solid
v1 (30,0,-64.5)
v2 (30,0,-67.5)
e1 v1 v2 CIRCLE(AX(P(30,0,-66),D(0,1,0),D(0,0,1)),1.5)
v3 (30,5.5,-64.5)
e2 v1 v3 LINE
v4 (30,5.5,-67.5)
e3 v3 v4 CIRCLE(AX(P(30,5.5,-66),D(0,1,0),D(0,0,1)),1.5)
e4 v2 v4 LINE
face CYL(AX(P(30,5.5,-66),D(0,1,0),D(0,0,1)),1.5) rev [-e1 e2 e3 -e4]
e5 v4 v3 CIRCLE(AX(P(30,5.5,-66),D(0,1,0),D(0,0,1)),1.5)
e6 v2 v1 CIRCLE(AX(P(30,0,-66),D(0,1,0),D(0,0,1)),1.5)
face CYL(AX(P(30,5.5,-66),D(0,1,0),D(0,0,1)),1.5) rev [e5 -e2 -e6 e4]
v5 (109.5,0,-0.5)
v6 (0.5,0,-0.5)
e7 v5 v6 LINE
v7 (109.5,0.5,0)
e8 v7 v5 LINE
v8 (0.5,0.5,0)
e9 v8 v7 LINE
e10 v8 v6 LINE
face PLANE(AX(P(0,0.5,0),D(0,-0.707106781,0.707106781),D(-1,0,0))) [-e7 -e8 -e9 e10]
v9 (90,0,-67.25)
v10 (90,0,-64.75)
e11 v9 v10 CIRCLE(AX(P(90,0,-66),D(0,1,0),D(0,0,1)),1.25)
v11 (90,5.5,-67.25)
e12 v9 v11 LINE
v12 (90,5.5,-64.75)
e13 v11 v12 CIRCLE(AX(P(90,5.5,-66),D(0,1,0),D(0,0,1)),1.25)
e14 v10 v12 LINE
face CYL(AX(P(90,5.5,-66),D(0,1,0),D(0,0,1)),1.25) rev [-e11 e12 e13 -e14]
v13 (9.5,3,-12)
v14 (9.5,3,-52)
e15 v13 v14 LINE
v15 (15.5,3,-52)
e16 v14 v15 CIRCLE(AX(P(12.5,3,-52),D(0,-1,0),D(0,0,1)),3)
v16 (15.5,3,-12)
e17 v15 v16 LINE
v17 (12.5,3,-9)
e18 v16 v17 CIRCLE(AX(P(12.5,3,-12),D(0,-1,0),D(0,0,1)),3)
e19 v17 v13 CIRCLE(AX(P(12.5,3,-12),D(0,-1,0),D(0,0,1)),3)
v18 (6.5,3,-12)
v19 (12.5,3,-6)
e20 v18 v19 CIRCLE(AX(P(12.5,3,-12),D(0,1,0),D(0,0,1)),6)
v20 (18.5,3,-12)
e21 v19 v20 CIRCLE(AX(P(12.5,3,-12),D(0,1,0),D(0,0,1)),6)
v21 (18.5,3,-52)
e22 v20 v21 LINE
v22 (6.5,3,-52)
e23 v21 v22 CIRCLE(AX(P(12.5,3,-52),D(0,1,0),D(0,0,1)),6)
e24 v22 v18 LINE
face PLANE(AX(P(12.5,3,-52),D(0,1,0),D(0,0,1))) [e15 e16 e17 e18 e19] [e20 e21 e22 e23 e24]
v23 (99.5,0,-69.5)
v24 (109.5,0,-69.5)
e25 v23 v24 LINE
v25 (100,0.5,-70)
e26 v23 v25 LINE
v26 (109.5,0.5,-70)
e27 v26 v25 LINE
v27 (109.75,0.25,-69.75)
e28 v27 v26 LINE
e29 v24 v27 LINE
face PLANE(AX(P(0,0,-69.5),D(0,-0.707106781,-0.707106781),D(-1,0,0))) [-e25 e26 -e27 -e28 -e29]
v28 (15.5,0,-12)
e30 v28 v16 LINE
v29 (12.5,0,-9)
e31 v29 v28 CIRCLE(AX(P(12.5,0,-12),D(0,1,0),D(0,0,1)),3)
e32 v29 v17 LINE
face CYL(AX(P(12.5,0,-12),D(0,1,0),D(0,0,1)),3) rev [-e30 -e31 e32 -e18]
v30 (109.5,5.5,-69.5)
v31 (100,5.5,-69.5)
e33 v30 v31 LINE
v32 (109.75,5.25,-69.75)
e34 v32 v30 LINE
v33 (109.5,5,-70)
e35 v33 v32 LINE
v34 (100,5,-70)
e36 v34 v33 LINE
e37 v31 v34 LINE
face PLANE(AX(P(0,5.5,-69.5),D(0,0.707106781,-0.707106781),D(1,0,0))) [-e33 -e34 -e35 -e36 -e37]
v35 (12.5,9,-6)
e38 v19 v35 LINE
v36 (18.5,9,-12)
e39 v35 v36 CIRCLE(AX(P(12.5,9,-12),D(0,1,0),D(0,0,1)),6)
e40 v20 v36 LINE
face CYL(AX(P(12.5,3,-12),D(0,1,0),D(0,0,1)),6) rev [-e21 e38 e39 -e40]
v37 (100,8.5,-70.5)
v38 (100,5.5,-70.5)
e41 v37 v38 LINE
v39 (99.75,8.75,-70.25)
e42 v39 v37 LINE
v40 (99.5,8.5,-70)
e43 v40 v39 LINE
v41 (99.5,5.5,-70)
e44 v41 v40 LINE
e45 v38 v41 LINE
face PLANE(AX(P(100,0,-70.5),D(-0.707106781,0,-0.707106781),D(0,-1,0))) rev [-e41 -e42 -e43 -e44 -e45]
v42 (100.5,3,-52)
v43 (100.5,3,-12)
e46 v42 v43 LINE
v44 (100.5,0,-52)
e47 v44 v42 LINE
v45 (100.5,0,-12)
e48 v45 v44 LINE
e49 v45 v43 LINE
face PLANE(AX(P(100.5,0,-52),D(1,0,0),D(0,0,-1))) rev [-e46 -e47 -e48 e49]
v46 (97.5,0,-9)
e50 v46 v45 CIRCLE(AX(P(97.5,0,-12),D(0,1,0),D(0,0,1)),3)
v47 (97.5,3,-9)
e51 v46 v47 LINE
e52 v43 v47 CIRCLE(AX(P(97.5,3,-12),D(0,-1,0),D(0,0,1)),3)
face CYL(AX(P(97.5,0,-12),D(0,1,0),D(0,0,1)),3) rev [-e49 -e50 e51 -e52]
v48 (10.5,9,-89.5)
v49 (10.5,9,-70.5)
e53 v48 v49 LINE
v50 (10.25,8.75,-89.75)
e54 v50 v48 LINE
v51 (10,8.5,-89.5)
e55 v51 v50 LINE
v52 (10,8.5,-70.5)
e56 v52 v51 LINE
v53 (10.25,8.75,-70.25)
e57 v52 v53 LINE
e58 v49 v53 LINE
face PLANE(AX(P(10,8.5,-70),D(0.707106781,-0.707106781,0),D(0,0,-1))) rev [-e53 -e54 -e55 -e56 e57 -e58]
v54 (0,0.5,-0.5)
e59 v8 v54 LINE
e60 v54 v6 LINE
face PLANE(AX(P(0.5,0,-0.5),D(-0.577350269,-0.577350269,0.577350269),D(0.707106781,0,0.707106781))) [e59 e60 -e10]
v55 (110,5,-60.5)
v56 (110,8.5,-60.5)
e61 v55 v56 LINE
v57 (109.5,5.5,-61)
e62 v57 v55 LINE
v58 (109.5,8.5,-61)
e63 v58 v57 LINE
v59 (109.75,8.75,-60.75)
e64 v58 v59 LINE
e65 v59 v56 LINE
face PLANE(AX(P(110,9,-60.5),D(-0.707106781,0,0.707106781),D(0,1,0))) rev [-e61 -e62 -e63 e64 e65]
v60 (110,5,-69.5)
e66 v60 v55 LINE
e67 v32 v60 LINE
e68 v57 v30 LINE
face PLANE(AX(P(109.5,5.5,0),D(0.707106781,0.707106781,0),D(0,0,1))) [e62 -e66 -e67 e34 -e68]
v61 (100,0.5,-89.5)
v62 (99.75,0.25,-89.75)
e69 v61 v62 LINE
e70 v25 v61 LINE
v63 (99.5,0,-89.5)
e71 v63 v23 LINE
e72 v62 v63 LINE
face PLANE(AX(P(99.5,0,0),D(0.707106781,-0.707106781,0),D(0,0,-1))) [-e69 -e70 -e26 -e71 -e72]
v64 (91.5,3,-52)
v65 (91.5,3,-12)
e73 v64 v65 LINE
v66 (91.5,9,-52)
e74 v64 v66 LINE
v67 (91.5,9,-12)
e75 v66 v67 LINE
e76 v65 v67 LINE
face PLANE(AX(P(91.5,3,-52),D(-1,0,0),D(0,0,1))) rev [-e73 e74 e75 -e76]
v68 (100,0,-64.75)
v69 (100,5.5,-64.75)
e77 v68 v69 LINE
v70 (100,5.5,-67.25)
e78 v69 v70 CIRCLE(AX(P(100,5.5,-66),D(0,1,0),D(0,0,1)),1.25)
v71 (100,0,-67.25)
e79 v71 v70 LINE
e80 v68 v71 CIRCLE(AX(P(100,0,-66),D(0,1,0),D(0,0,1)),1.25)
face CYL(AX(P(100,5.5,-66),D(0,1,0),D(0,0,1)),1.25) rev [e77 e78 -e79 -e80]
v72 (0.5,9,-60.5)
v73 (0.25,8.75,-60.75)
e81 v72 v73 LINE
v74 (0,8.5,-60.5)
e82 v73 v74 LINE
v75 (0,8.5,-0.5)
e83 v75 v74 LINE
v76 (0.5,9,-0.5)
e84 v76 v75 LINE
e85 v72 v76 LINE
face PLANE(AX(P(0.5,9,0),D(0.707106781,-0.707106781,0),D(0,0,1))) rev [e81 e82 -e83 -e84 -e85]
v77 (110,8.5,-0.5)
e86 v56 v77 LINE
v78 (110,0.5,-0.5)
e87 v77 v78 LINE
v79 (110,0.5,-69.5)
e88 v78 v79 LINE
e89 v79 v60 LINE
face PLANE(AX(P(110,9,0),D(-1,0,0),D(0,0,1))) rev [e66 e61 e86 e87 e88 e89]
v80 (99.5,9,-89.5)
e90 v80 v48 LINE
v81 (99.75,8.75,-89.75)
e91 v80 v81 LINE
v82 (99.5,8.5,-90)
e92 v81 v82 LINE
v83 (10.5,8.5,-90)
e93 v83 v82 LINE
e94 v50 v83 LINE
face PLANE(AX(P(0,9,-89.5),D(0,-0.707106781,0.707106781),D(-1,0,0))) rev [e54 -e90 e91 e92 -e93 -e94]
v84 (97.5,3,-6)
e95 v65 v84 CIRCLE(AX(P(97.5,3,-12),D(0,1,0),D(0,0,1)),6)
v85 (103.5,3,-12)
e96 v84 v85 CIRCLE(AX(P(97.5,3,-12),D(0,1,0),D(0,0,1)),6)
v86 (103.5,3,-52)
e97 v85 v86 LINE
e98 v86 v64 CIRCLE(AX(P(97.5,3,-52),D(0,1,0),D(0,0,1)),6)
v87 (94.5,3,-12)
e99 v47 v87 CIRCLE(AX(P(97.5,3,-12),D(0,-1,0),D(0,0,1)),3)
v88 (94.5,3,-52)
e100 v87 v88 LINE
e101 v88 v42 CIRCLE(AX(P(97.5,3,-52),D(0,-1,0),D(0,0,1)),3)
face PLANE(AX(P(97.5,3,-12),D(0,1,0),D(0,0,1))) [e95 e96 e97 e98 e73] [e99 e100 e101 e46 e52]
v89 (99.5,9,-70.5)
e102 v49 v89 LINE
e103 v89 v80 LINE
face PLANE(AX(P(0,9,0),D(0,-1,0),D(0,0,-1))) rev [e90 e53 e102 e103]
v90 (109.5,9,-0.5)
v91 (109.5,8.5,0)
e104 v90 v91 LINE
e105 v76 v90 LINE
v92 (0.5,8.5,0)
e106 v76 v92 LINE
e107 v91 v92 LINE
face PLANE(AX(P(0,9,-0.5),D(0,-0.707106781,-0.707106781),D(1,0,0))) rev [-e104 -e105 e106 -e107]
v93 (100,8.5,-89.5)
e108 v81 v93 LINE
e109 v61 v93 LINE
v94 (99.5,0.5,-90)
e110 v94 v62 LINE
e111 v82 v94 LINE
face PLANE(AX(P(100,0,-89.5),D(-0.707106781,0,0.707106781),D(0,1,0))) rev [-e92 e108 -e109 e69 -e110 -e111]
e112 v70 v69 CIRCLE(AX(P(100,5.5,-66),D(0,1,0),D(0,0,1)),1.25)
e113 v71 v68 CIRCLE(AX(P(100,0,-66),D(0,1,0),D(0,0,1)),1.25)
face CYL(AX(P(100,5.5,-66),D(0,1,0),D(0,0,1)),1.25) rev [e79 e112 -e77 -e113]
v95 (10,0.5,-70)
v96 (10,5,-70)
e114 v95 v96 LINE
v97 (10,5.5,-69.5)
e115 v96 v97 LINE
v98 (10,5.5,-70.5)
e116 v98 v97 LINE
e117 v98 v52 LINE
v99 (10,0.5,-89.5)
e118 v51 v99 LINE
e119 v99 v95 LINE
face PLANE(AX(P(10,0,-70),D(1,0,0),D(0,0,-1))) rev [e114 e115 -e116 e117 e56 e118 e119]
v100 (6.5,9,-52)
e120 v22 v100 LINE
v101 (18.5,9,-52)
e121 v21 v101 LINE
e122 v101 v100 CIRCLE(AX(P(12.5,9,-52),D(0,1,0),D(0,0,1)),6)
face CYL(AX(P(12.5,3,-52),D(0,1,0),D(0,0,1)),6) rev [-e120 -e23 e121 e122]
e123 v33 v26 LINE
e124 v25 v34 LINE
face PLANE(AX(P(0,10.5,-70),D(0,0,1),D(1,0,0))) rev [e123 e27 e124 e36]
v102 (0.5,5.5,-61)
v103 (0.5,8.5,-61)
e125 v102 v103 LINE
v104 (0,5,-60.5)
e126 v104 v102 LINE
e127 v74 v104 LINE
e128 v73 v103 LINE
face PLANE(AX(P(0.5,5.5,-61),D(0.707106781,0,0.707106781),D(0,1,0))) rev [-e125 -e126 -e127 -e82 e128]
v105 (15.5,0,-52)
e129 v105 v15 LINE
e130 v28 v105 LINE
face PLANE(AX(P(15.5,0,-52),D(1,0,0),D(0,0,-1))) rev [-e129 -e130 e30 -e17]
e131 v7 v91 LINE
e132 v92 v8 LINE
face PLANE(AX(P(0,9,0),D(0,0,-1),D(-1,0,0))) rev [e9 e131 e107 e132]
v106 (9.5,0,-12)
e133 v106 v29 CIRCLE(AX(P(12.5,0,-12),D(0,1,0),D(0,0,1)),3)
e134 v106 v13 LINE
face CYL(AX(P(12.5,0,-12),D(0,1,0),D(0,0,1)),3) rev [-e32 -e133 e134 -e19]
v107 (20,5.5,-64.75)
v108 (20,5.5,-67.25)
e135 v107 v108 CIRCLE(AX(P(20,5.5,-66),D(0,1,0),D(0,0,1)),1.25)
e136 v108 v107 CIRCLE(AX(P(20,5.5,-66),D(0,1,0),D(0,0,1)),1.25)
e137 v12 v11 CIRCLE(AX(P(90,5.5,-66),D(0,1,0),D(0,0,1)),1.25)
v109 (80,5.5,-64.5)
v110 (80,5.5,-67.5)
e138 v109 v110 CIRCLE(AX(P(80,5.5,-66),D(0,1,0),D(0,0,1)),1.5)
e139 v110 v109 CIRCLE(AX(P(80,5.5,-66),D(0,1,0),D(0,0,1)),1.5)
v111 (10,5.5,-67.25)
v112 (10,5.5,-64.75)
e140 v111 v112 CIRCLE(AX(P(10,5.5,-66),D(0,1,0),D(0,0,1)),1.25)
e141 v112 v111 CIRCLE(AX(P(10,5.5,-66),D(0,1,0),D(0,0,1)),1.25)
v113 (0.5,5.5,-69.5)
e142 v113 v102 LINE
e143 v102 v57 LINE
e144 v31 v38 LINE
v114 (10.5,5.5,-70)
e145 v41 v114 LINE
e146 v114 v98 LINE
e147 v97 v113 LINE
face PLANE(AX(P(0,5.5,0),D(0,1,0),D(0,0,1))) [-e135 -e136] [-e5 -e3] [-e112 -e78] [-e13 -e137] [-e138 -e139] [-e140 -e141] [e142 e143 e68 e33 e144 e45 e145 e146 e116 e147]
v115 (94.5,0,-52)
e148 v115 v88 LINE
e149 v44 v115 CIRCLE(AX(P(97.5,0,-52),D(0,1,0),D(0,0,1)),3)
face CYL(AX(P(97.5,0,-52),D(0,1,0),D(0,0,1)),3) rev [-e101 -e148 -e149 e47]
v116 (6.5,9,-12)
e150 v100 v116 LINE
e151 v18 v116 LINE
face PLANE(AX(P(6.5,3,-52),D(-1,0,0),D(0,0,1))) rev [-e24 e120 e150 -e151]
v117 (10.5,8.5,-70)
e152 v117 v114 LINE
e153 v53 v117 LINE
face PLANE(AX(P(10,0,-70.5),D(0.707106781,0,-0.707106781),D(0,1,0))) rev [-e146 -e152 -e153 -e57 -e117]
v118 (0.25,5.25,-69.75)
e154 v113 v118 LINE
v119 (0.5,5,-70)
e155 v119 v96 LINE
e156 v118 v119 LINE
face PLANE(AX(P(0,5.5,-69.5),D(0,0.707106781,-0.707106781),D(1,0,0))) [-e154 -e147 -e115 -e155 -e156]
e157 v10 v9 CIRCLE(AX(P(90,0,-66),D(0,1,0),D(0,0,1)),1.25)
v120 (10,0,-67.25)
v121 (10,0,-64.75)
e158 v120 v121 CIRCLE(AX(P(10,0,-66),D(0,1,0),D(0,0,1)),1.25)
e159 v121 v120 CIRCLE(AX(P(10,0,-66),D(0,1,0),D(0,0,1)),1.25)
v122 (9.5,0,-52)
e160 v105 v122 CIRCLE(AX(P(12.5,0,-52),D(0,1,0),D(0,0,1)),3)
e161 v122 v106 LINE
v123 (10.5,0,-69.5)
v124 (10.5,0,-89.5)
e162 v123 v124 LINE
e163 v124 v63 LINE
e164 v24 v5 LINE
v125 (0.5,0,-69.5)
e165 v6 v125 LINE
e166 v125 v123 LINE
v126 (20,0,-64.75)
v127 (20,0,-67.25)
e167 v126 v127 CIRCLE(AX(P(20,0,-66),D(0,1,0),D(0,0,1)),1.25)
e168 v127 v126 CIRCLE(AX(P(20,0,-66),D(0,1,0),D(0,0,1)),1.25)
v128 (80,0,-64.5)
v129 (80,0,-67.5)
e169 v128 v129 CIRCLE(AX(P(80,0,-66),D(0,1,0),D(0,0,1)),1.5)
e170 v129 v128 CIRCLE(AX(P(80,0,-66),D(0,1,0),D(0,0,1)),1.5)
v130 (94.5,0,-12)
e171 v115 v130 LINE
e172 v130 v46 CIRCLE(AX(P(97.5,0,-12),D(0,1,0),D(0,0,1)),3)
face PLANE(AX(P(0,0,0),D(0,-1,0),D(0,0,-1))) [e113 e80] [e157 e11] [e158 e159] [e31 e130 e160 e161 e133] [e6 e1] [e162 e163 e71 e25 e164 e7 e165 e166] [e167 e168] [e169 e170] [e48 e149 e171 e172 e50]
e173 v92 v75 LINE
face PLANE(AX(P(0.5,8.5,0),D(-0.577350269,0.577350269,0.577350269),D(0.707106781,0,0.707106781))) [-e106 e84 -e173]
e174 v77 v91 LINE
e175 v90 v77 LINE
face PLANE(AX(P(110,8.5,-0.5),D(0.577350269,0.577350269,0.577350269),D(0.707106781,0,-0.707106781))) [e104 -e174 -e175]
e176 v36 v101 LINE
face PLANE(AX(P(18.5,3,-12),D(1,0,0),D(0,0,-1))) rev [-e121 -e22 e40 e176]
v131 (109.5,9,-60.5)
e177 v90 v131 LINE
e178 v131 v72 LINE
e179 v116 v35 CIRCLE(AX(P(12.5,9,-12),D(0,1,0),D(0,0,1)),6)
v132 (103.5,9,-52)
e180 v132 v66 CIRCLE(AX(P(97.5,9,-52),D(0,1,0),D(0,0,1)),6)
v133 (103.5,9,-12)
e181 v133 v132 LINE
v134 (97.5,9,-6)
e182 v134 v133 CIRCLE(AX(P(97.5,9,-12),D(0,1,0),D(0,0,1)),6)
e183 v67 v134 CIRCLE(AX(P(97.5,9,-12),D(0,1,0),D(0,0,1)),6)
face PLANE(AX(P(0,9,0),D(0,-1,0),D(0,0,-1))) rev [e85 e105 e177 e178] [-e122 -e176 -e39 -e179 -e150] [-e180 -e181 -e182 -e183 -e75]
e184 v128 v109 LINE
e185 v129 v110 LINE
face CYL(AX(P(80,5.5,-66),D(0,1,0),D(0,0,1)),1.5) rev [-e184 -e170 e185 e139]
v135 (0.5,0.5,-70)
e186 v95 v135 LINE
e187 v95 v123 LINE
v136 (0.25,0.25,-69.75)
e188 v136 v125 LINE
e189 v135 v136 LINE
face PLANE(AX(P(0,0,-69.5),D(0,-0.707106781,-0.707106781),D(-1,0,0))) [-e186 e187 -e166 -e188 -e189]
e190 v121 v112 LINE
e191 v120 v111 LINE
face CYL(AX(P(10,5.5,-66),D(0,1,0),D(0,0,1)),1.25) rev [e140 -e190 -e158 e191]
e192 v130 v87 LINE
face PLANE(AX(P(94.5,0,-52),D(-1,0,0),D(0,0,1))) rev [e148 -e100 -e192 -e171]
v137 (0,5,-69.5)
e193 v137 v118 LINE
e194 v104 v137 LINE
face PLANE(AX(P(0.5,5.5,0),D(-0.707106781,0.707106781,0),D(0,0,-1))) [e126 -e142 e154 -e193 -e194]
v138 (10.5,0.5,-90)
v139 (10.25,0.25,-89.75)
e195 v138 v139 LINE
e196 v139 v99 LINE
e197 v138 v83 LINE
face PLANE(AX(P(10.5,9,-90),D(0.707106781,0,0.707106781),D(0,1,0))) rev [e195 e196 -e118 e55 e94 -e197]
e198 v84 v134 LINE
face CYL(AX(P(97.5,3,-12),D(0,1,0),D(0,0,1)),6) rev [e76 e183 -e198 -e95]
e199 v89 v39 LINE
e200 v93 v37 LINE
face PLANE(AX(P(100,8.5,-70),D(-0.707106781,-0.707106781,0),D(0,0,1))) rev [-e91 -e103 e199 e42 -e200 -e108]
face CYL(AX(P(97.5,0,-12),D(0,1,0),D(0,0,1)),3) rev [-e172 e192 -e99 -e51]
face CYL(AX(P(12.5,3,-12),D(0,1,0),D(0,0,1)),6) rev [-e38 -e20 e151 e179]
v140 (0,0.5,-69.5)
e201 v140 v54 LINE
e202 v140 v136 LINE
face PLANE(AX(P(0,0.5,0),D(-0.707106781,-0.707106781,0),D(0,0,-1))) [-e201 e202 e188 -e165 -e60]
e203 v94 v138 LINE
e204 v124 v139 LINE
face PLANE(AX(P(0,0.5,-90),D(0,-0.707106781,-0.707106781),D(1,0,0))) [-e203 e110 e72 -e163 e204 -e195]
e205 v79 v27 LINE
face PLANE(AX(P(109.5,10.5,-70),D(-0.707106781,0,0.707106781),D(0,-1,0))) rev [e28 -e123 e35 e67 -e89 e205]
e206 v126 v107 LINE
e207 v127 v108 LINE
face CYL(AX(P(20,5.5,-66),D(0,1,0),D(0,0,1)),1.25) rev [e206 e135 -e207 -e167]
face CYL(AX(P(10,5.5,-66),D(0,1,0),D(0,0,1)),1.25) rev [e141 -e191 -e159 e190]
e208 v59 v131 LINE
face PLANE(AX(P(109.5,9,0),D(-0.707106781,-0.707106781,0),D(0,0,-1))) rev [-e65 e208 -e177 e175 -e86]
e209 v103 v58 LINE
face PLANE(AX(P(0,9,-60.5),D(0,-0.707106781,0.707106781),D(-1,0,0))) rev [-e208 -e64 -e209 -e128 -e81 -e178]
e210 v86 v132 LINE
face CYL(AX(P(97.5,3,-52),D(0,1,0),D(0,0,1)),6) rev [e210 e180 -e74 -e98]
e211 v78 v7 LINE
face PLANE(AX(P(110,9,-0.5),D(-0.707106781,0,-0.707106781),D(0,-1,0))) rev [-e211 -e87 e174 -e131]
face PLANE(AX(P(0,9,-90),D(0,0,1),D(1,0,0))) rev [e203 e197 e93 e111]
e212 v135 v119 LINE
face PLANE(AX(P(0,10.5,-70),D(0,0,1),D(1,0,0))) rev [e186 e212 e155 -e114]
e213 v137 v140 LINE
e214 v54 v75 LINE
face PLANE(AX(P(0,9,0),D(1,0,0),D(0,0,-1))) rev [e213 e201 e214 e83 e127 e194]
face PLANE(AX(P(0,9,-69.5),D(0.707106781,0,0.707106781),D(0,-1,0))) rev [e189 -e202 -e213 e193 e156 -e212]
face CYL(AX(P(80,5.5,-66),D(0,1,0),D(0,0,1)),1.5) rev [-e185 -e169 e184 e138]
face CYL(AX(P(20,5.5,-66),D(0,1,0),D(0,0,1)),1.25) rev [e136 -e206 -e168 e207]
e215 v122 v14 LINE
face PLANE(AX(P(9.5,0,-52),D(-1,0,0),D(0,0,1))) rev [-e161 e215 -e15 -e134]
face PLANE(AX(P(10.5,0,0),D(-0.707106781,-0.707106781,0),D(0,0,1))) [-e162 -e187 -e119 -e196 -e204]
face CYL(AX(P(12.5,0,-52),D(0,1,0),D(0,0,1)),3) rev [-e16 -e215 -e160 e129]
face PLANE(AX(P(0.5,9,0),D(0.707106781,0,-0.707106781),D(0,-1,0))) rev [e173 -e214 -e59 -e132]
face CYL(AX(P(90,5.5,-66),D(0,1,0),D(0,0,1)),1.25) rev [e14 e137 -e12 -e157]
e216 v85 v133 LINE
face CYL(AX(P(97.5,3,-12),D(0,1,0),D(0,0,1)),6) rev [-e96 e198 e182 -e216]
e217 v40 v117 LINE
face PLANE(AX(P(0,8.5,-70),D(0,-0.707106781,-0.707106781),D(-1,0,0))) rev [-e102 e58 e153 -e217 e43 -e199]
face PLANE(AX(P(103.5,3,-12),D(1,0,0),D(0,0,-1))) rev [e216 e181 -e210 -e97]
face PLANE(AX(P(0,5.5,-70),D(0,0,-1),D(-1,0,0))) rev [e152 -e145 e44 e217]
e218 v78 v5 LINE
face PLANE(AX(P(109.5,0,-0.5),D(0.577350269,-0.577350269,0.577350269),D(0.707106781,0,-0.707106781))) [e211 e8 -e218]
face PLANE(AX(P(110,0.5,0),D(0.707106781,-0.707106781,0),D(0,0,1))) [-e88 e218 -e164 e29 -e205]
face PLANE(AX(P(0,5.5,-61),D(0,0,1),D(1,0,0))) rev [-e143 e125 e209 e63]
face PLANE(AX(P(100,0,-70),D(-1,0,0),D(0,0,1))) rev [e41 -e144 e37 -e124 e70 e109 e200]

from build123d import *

# Parameters (mm, degrees)
SKETCH1_W             = 110
SKETCH1_H             = 90
BOSS_EXTRUDE1_DEPTH   = 9
SKETCH2_W             = 110
SKETCH2_H             = 8
BOSS_EXTRUDE2_DEPTH   = 1.5
SKETCH5_W             = 20
SKETCH5_H             = 20
BOSS_EXTRUDE3_DEPTH   = 9
CUT_EXTRUDE1_DEPTH    = 156.823618235
CUT_EXTRUDE2_DEPTH    = 6
SKETCH6_W             = 10
SKETCH6_H             = 40
CUT_EXTRUDE3_DEPTH    = 156.823618235
SKETCH8_W             = 110
SKETCH8_H             = 9
CUT_EXTRUDE5_DEPTH    = 5
M3_TAPPED_HOLE1_D     = 2.5
MOVE_FACE1_BY         = 20
MOVE_FACE1_2_BY       = 20
F_3_0MM_DOWEL_HOLE1_D = 3
CHAMFER1_SIZE         = 0.5
CHAMFER3_SIZE         = 0.5
CHAMFER4_SIZE         = 0.5


with BuildPart() as part:
    # Sketch1 → Boss-Extrude1 (new body)
    with BuildSketch(Plane(origin=(0, 0, 0), x_dir=(1, 0, 0), z_dir=(0, 1, 0))):
        with Locations((55, 45)):
            Rectangle(SKETCH1_W, SKETCH1_H)
    extrude(amount=BOSS_EXTRUDE1_DEPTH)

    # Sketch2 → Boss-Extrude2 (add)
    with BuildSketch(Plane(origin=(0, 9, 0), x_dir=(1, 0, 0), z_dir=(0, 1, 0))):
        with Locations((55, 66)):
            Rectangle(SKETCH2_W, SKETCH2_H)
    extrude(amount=BOSS_EXTRUDE2_DEPTH)

    # Sketch5 → Boss-Extrude3 (add)
    with BuildSketch(Plane.XZ):
        with Locations((10, -100)):
            Rectangle(SKETCH5_W, SKETCH5_H)
        with Locations((100, -100)):
            Rectangle(SKETCH5_W, SKETCH5_H)
    extrude(amount=-BOSS_EXTRUDE3_DEPTH)

    # Sketch3 → Cut-Extrude1 (cut, through all)
    with BuildSketch(Plane(origin=(0, 9, 0), x_dir=(1, 0, 0), z_dir=(0, 1, 0))):
        with BuildLine():
            Line((15.5, 52), (15.5, 12))
            ThreePointArc((15.5, 12), (12.5, 9), (9.5, 12))
            Line((9.5, 12), (9.5, 52))
            ThreePointArc((9.5, 52), (12.5, 55), (15.5, 52))
        make_face()
        with BuildLine():
            Line((94.5, 52), (94.5, 12))
            ThreePointArc((94.5, 12), (97.5, 9), (100.5, 12))
            Line((100.5, 12), (100.5, 52))
            ThreePointArc((100.5, 52), (97.5, 55), (94.5, 52))
        make_face()
    extrude(amount=-CUT_EXTRUDE1_DEPTH, mode=Mode.SUBTRACT)

    # Sketch4 → Cut-Extrude2 (cut)
    with BuildSketch(Plane(origin=(0, 9, 0), x_dir=(1, 0, 0), z_dir=(0, 1, 0))):
        with BuildLine():
            Line((6.5, 52), (6.5, 12))
            ThreePointArc((6.5, 12), (12.5, 6), (18.5, 12))
            Line((18.5, 12), (18.5, 52))
            ThreePointArc((18.5, 52), (12.5, 58), (6.5, 52))
        make_face()
        with BuildLine():
            Line((103.5, 12), (103.5, 52))
            ThreePointArc((103.5, 52), (97.5, 58), (91.5, 52))
            Line((91.5, 52), (91.5, 12))
            ThreePointArc((91.5, 12), (97.5, 6), (103.5, 12))
        make_face()
    extrude(amount=-CUT_EXTRUDE2_DEPTH, mode=Mode.SUBTRACT)

    # Sketch6 → Cut-Extrude3 (cut, through all)
    with BuildSketch(Plane(origin=(0, 9, 0), x_dir=(1, 0, 0), z_dir=(0, 1, 0))):
        with Locations((5, 90)):
            Rectangle(SKETCH6_W, SKETCH6_H)
        with Locations((105, 90)):
            Rectangle(SKETCH6_W, SKETCH6_H)
    extrude(amount=-CUT_EXTRUDE3_DEPTH, mode=Mode.SUBTRACT)

    # Sketch8 → Cut-Extrude5 (cut)
    with BuildSketch(Plane(origin=(0, 10.5, 0), x_dir=(1, 0, 0), z_dir=(0, 1, 0))):
        with Locations((55, 65.5)):
            Rectangle(SKETCH8_W, SKETCH8_H)
    extrude(amount=-CUT_EXTRUDE5_DEPTH, mode=Mode.SUBTRACT)

    # M3 Tapped Hole1 (through all)
    with Locations(Plane(origin=(0, 5.5, 0), x_dir=(1, 0, 0), z_dir=(0, 1, 0))):
        with Locations((10, 66), (100, 66), (20, 66), (90, 66)):
            Hole(M3_TAPPED_HOLE1_D / 2)

    # Move Face1: a face moved inward by 20.0
    extrude(part.faces().sort_by_distance((95, 4.5, -110))[0], amount=MOVE_FACE1_BY, dir=(0, 0, 1), mode=Mode.SUBTRACT)

    # Move Face1 2: a face moved inward by 20.0
    extrude(part.faces().sort_by_distance((15, 4.5, -110))[0], amount=MOVE_FACE1_2_BY, dir=(0, 0, 1), mode=Mode.SUBTRACT)

    # Ø3.0mm dowel hole1 (through all)
    with Locations(Plane(origin=(0, 5.5, 0), x_dir=(1, 0, 0), z_dir=(0, 1, 0))):
        with Locations((30, 66), (80, 66)):
            Hole(F_3_0MM_DOWEL_HOLE1_D / 2)

    # Chamfer1
    chamfer1_edges = [part.edges().sort_by_distance(p)[0] for p in [
        (0, 0, -35),
        (110, 9, -30.5),
        (10, 4.5, -90),
        (100, 4.5, -90),
        (110, 2.75, -70),
        (0, 2.75, -70),
        (0, 9, -30.5),
        (110, 7.25, -61),
        (0, 7.25, -61),
        (0, 5.5, -65.5),
        (110, 5.5, -65.5),
        (55, 9, -90),
        (55, 0, -90),
        (110, 0, -35),
        (55, 0, 0),
        (110, 4.5, 0),
        (0, 4.5, 0),
        (55, 9, 0),
    ]]
    chamfer(chamfer1_edges, length=CHAMFER1_SIZE)

    # Chamfer3
    chamfer3_edges = [part.edges().sort_by_distance(p)[0] for p in [
        (55, 9, -70),
        (10, 0, -79.75),
        (10, 9, -79.75),
        (104.75, 0, -70),
        (5.25, 5.5, -70),
        (100, 0, -79.75),
        (5.25, 0, -70),
        (100, 9, -79.75),
        (104.75, 5.5, -70),
        (55, 9, -61),
    ]]
    chamfer(chamfer3_edges, length=CHAMFER3_SIZE)

    # Chamfer4
    chamfer4_edges = [part.edges().sort_by_distance(p)[0] for p in [
        (10, 7, -70),
        (100, 7, -70),
    ]]
    chamfer(chamfer4_edges, length=CHAMFER4_SIZE)


solid = part.part
